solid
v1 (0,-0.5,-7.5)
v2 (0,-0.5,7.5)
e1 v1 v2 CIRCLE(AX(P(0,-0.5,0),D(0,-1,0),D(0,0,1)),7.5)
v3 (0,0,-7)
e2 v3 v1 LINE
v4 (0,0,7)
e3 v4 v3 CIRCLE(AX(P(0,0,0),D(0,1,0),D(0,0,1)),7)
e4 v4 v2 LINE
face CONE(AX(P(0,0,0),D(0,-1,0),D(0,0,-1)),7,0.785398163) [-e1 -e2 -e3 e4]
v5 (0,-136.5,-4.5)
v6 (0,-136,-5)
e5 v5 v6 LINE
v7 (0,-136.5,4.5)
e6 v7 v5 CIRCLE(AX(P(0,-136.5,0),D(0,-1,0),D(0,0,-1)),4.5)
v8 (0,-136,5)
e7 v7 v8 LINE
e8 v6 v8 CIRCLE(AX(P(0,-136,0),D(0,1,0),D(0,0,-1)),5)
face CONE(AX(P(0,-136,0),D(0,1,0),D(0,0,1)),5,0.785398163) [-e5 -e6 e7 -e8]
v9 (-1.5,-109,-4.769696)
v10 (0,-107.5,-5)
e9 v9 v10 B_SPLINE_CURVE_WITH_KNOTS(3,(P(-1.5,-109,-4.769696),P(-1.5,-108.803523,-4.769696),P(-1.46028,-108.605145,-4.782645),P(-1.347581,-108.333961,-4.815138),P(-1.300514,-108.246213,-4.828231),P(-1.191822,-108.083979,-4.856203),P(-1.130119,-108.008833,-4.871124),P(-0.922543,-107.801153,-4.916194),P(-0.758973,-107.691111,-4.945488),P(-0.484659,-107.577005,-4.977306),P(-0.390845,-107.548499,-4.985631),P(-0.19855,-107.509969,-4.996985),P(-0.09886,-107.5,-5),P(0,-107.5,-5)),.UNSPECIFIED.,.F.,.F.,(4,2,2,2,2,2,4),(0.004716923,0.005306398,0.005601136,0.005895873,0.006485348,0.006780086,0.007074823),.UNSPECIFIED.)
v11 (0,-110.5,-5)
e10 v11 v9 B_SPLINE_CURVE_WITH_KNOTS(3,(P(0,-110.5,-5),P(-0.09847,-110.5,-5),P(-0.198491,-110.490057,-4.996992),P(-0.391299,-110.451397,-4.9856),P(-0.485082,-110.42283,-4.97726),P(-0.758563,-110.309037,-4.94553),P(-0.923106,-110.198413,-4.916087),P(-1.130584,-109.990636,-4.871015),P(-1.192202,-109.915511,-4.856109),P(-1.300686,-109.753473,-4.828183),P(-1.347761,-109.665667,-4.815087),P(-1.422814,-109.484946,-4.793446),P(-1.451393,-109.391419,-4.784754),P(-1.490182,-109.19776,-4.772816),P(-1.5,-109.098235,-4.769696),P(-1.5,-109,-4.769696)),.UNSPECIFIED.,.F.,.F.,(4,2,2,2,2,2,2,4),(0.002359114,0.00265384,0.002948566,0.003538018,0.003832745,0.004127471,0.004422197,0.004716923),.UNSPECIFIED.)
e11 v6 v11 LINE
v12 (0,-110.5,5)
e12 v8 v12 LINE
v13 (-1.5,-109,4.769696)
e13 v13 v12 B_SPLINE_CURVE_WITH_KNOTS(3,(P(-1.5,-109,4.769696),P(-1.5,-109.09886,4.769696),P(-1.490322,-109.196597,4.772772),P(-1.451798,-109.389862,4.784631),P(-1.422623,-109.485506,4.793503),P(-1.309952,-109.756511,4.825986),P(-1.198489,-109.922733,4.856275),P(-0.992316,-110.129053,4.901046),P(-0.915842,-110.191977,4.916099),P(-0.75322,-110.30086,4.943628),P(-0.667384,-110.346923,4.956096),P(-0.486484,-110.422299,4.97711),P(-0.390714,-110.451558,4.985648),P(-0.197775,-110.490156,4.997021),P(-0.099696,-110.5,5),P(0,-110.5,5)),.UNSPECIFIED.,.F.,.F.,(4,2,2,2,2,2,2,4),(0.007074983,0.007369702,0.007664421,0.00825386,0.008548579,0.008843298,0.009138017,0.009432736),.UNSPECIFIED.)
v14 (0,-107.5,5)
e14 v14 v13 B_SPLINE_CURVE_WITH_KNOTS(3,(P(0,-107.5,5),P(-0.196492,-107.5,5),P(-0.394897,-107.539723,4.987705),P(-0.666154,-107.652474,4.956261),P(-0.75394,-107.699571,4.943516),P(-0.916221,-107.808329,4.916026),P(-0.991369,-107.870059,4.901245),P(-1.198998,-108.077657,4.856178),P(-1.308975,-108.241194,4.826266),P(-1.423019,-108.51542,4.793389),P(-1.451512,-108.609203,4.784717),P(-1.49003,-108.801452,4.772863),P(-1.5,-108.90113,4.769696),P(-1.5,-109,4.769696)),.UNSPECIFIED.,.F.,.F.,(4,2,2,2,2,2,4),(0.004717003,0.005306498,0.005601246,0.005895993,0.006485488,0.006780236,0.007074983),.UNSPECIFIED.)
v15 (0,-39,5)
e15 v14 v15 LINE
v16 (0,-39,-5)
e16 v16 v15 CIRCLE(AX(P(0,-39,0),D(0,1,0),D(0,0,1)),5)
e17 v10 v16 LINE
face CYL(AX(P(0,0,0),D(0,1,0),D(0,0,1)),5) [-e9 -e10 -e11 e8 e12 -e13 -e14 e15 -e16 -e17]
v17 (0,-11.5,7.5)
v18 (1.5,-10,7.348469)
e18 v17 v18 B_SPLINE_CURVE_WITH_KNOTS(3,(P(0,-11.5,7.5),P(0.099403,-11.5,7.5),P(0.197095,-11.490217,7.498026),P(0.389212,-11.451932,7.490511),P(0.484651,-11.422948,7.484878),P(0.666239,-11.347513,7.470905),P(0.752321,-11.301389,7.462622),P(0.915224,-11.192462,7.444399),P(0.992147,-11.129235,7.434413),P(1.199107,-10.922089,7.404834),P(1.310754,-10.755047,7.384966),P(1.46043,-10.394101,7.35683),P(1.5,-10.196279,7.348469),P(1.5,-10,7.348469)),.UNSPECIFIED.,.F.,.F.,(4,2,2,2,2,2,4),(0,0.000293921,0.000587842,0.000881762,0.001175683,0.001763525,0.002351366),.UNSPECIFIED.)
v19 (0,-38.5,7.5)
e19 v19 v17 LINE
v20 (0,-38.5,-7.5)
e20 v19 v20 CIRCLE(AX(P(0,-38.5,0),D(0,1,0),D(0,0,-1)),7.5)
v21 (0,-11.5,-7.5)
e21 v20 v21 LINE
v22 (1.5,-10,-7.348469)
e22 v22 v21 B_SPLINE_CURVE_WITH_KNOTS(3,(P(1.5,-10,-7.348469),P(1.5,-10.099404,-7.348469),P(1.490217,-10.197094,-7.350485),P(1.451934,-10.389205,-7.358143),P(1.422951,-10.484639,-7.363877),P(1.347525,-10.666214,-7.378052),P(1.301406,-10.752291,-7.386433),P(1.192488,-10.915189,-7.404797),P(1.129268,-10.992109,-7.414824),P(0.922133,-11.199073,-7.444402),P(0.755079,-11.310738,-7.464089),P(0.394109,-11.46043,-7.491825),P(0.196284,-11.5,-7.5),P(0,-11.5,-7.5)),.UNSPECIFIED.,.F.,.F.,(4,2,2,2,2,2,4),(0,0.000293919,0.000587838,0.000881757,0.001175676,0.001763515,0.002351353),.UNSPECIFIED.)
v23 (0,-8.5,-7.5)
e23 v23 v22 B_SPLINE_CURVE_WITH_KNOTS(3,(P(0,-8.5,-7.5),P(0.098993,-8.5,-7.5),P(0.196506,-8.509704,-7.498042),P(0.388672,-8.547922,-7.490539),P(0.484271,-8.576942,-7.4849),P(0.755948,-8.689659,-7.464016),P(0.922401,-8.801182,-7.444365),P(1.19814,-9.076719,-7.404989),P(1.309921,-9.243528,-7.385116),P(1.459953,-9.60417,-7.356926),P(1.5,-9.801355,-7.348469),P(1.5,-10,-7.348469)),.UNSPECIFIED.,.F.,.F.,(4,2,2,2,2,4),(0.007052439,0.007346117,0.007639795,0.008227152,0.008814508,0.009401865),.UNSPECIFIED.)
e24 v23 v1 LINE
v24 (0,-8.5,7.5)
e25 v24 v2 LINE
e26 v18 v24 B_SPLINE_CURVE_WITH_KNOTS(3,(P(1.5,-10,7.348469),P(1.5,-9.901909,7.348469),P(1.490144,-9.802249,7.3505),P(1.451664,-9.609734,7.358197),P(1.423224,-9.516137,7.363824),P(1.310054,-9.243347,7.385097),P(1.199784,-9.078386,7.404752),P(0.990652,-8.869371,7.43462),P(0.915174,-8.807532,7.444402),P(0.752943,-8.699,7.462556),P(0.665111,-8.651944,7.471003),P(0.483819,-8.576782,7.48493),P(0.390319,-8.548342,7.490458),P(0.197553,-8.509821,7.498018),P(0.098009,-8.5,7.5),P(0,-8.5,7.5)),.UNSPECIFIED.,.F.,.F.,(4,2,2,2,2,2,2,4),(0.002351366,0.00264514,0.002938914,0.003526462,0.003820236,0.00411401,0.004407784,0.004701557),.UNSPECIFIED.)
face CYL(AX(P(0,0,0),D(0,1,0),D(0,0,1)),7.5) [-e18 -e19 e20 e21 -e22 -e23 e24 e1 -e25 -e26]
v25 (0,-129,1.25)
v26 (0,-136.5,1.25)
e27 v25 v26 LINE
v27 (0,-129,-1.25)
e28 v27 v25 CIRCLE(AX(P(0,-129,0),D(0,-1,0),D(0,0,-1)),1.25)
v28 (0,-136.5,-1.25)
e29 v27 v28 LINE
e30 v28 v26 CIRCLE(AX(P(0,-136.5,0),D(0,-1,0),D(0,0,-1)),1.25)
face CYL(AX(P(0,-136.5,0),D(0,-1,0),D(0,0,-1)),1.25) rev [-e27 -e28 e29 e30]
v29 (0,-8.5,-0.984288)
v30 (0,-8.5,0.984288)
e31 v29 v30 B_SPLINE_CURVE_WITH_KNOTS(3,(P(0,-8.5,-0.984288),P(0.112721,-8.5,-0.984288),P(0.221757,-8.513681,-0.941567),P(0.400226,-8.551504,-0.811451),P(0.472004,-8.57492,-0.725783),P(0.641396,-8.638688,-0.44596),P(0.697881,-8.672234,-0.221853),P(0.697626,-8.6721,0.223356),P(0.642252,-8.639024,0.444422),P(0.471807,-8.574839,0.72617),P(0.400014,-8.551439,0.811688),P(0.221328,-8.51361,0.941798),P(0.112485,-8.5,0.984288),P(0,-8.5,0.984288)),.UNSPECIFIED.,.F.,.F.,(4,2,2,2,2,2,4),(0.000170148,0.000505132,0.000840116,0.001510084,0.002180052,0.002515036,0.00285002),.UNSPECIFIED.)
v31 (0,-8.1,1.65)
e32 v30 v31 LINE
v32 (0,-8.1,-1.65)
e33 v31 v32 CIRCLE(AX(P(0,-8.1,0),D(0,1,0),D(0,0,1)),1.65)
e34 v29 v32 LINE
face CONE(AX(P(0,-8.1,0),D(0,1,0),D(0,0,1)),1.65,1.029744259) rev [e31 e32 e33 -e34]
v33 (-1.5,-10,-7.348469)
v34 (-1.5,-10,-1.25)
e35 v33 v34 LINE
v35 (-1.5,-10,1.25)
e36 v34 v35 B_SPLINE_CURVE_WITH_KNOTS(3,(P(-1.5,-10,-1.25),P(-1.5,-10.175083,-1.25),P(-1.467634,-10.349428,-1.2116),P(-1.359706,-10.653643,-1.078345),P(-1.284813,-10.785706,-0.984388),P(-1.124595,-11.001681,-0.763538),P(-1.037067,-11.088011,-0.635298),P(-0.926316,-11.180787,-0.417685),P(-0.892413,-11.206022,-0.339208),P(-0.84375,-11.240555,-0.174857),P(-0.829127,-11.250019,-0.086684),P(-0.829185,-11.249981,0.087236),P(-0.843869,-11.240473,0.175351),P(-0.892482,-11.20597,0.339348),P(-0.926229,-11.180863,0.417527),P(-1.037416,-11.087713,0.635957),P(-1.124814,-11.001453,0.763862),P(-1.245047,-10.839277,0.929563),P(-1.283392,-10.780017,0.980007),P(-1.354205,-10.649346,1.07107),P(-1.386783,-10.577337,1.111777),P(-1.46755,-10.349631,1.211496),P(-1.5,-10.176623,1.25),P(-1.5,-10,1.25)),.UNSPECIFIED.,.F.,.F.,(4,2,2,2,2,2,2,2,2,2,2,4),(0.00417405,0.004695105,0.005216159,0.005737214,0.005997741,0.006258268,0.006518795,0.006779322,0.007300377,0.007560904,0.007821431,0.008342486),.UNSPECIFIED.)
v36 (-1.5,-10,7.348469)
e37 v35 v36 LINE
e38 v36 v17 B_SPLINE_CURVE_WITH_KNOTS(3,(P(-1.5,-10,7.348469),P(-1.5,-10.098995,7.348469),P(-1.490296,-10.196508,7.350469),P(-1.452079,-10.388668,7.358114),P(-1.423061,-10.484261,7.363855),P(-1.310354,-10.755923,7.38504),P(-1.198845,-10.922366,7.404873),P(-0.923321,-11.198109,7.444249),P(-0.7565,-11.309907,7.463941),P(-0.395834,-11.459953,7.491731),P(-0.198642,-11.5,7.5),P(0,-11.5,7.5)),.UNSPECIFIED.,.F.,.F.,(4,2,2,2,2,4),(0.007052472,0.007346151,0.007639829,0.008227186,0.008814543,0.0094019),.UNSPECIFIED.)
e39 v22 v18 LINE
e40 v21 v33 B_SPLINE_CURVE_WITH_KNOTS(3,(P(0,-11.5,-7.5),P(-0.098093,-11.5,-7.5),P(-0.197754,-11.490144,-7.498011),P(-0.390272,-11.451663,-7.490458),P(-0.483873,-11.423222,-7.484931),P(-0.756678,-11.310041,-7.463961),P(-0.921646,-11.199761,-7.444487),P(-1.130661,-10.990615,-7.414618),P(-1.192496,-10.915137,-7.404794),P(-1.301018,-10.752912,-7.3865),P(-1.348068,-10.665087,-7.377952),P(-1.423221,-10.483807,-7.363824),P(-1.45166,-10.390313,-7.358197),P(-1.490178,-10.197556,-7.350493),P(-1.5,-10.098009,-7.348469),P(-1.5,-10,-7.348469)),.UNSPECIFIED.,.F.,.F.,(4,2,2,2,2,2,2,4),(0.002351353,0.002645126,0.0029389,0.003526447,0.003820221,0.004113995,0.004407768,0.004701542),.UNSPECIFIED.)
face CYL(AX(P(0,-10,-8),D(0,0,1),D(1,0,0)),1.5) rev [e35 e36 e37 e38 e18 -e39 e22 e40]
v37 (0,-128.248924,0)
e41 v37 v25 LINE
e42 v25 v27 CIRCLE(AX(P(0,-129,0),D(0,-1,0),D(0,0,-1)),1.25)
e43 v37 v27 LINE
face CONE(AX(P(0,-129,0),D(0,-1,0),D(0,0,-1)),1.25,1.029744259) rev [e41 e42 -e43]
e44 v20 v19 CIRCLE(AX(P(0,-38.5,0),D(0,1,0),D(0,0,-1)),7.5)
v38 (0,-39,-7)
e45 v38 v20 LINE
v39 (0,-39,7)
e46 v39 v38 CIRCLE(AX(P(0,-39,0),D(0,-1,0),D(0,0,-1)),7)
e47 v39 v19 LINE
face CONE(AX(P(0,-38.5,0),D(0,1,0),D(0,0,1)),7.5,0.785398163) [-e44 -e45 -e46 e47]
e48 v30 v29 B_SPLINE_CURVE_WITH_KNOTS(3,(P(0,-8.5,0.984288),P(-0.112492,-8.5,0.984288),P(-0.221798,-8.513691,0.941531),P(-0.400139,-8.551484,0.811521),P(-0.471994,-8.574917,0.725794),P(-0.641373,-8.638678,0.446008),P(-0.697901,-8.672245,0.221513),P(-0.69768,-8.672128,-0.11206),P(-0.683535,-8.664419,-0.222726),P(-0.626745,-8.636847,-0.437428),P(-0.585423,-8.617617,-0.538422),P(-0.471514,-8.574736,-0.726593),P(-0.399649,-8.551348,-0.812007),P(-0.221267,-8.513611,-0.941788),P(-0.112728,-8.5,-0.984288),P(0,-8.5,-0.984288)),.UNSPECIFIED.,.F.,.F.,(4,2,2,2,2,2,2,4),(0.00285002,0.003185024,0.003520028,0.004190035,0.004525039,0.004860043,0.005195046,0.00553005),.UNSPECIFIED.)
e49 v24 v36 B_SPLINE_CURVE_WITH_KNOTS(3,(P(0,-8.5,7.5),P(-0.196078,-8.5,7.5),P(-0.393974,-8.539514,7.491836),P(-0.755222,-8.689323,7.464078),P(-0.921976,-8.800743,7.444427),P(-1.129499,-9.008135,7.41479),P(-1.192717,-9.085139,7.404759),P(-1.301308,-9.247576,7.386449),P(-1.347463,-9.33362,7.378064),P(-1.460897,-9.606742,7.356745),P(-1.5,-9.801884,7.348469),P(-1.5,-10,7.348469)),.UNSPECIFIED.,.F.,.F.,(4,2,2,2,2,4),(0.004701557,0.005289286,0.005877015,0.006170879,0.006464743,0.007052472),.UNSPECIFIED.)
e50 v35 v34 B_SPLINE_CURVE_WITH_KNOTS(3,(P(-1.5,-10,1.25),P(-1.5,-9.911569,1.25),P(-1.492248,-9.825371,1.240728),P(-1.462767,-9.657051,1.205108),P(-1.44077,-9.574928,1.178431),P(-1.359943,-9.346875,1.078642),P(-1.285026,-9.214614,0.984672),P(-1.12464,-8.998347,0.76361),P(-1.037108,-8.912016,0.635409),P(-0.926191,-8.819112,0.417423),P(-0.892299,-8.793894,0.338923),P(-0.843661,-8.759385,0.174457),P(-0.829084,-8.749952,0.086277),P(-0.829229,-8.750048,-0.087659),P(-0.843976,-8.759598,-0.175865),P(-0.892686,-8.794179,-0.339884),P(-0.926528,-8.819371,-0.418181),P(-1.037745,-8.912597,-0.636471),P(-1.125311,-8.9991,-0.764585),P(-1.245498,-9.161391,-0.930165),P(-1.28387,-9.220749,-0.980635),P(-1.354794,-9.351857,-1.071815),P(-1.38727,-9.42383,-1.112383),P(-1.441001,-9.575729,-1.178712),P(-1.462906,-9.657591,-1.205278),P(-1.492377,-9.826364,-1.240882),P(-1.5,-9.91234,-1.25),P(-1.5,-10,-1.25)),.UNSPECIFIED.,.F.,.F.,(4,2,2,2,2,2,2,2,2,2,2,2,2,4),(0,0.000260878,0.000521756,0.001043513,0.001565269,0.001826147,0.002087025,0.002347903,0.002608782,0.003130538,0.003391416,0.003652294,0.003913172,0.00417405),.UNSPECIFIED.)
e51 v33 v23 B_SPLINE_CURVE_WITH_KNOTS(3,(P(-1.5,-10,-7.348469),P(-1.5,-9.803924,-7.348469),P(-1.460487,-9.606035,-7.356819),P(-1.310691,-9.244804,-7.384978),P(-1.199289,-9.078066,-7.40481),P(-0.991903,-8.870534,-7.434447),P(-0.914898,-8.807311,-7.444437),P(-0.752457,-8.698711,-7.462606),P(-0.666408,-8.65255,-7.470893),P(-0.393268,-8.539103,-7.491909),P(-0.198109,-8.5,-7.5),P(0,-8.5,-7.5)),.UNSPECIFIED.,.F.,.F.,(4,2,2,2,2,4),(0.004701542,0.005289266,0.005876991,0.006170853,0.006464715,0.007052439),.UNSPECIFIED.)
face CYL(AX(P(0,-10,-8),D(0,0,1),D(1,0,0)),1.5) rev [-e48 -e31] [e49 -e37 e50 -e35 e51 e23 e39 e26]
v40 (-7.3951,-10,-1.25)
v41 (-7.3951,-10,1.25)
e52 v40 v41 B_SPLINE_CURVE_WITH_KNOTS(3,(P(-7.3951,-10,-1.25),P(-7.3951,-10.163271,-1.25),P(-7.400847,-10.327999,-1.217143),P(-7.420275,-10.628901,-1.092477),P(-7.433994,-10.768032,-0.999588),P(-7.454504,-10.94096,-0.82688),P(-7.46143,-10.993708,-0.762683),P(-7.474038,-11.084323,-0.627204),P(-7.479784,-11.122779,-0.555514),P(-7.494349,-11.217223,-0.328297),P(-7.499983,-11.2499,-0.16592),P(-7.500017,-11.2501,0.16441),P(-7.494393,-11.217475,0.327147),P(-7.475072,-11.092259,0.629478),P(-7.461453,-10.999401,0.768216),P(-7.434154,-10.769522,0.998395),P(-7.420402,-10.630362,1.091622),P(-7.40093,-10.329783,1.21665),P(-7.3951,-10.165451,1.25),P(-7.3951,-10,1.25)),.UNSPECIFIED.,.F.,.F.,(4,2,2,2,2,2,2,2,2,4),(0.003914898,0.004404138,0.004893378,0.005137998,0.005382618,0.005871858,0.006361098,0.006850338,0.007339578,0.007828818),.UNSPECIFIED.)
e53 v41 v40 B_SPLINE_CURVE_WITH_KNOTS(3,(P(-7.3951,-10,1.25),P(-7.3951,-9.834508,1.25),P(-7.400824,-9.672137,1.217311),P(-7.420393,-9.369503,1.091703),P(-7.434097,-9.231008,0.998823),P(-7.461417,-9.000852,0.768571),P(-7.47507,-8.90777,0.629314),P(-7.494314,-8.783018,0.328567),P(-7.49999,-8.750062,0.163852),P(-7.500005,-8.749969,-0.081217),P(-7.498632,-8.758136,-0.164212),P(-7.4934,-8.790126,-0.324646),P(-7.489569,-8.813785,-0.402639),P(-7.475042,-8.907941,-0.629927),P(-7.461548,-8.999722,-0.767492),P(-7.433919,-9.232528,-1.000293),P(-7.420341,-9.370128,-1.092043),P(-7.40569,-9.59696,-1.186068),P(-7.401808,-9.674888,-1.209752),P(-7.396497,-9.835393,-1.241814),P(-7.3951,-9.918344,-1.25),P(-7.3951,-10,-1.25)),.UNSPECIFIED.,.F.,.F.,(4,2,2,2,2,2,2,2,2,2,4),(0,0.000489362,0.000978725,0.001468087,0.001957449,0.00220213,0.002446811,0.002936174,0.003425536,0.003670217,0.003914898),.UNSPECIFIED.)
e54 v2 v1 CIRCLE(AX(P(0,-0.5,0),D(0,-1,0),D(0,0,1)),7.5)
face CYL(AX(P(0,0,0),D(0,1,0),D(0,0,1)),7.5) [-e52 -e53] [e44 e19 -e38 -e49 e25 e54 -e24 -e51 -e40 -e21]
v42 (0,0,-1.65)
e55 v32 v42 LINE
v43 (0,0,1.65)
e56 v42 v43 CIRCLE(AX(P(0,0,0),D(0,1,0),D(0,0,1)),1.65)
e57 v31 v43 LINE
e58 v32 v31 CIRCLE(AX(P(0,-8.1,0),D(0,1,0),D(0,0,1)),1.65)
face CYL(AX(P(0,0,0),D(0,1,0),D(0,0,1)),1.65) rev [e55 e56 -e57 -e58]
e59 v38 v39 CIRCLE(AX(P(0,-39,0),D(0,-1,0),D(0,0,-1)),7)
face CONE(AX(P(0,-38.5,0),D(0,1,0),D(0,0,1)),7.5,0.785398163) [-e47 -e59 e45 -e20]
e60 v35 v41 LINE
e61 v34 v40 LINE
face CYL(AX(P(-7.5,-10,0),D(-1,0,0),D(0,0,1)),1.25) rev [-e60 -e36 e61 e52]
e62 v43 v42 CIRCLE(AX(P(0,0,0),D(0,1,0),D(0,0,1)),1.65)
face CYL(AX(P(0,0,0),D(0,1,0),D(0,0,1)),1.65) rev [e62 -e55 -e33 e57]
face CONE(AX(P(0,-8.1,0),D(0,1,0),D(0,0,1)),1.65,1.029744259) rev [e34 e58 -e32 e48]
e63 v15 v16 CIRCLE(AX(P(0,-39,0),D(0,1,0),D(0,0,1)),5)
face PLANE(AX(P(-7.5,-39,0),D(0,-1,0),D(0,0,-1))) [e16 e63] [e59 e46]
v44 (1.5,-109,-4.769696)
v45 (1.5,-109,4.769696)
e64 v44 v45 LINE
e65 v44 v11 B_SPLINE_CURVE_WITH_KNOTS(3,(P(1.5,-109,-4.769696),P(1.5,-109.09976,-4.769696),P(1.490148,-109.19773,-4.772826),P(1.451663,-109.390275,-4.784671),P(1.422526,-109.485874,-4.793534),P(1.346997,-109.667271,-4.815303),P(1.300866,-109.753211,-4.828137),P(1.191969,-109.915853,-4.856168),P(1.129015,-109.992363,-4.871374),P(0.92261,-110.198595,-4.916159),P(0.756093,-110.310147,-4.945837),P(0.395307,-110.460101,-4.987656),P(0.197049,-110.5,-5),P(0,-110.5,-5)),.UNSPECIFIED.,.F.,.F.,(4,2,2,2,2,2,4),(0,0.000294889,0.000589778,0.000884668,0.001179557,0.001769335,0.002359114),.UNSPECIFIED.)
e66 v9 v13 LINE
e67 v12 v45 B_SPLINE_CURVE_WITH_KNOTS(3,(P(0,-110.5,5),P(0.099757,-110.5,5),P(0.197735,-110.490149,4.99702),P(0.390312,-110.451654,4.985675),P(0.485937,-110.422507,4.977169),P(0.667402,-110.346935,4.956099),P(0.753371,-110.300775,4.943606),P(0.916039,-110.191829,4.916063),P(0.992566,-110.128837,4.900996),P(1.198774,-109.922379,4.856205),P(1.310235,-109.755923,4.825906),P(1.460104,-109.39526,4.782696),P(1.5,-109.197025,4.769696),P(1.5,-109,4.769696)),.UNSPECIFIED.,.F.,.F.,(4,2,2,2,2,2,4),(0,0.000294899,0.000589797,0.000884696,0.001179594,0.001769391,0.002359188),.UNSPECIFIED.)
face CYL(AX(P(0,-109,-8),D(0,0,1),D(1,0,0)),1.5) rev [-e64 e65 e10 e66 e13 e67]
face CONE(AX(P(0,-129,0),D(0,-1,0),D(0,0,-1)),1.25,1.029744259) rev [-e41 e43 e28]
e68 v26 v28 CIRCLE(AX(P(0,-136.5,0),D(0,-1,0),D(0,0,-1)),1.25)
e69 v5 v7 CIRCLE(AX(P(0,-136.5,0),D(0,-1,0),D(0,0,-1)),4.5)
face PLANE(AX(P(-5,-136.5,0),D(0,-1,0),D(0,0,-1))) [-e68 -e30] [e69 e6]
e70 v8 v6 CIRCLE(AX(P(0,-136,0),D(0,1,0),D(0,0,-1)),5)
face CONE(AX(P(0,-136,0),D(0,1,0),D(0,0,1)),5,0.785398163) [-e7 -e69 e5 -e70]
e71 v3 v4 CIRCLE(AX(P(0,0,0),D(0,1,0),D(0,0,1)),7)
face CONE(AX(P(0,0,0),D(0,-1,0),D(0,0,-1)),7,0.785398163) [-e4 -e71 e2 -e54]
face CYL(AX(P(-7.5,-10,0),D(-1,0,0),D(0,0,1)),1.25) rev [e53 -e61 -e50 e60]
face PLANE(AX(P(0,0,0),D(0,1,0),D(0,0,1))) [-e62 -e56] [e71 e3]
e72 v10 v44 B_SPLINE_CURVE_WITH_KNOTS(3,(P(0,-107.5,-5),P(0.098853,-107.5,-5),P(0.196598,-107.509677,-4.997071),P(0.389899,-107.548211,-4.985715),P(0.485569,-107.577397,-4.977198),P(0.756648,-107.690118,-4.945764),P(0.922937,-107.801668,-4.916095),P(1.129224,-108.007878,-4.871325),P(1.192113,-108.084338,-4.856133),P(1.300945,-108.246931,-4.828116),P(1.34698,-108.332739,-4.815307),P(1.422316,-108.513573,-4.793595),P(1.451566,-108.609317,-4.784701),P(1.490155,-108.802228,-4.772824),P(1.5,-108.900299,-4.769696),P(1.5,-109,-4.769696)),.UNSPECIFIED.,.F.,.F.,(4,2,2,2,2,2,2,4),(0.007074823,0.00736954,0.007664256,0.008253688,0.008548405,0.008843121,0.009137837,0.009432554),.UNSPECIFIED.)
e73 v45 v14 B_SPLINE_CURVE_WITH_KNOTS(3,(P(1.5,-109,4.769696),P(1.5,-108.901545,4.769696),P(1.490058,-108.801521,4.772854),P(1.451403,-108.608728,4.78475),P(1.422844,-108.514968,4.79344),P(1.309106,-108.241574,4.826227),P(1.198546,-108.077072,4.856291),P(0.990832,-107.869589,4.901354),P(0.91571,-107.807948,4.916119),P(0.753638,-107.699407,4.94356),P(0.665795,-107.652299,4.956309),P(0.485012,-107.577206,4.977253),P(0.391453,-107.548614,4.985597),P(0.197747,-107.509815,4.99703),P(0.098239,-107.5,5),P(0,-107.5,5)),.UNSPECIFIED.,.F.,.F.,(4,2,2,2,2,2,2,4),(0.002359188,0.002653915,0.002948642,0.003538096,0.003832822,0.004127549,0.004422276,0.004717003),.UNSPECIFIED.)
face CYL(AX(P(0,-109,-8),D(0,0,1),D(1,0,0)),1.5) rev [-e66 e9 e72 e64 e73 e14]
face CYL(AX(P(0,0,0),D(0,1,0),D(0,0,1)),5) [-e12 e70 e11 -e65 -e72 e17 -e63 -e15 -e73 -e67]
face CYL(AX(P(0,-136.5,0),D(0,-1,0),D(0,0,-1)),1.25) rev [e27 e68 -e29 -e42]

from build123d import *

# Parameters (mm, degrees)
M4_TAPPED_HOLE1_D     = 3.3
M4_TAPPED_HOLE1_DEPTH = 8.1
M4_TAPPED_HOLE1_TIP   = 0.991420021
SKETCH3_R             = 1.5
CUT_EXTRUDE1_DEPTH    = 8
M3_TAPPED_HOLE2_D     = 2.5
M3_TAPPED_HOLE2_DEPTH = 7.5
M3_TAPPED_HOLE2_TIP   = 0.751075774
CHAMFER1_SIZE         = 0.5
M3_TAPPED_HOLE3_D     = 2.5
M3_TAPPED_HOLE3_DEPTH = 7.5
M3_TAPPED_HOLE3_TIP   = 0.751075774
SKETCH9_R             = 1.5
CUT_EXTRUDE2_DEPTH    = 8


with BuildPart() as part:
    # Sketch1 → Revolve1 (revolve)
    with BuildSketch(Plane.XY, mode=Mode.PRIVATE) as revolve1_sk:
        Polygon((0, 0), (-7.5, 0), (-7.5, -39), (-5, -39), (-5, -136.5), (0, -136.5), align=None)
    revolve(revolve1_sk.sketch.rotate(Axis((0, 0, 0), (0, -1, 0)), 270), axis=Axis((0, 0, 0), (0, -1, 0)))

    # M4 Tapped Hole1
    with Locations(Plane.ZX):
        with Locations((0, 0)):
            Hole(M4_TAPPED_HOLE1_D / 2, depth=M4_TAPPED_HOLE1_DEPTH)
            with Locations((0, 0, -(M4_TAPPED_HOLE1_DEPTH + M4_TAPPED_HOLE1_TIP / 2))):  # 118° drill point
                Cone(0, M4_TAPPED_HOLE1_D / 2, M4_TAPPED_HOLE1_TIP, mode=Mode.SUBTRACT)

    # Sketch3 → Cut-Extrude1 (cut, symmetric)
    with BuildSketch(Plane.XY):
        with Locations((0, -10)):
            Circle(SKETCH3_R)
    extrude(amount=CUT_EXTRUDE1_DEPTH, both=True, mode=Mode.SUBTRACT)

    # M3 Tapped Hole2
    with Locations(Plane(origin=(0, -136.5, 0), x_dir=(0, 0, -1), z_dir=(0, -1, 0))):
        with Locations((0, 0)):
            Hole(M3_TAPPED_HOLE2_D / 2, depth=M3_TAPPED_HOLE2_DEPTH)
            with Locations((0, 0, -(M3_TAPPED_HOLE2_DEPTH + M3_TAPPED_HOLE2_TIP / 2))):  # 118° drill point
                Cone(0, M3_TAPPED_HOLE2_D / 2, M3_TAPPED_HOLE2_TIP, mode=Mode.SUBTRACT)

    # Chamfer1
    chamfer1_edges = [part.edges().sort_by_distance(p)[0] for p in [
        (0, -136.5, -5),
        (0, -39, -7.5),
        (0, 0, -7.5),
    ]]
    chamfer(chamfer1_edges, length=CHAMFER1_SIZE)

    # M3 Tapped Hole3
    with Locations(Plane(origin=(-7.5, -10, 0), x_dir=(0, 0, -1), z_dir=(-1, 0, 0))):
        with Locations((0, 0)):
            Hole(M3_TAPPED_HOLE3_D / 2, depth=M3_TAPPED_HOLE3_DEPTH)
            with Locations((0, 0, -(M3_TAPPED_HOLE3_DEPTH + M3_TAPPED_HOLE3_TIP / 2))):  # 118° drill point
                Cone(0, M3_TAPPED_HOLE3_D / 2, M3_TAPPED_HOLE3_TIP, mode=Mode.SUBTRACT)

    # Sketch9 → Cut-Extrude2 (cut, symmetric)
    with BuildSketch(Plane.XY):
        with Locations((0, -109)):
            Circle(SKETCH9_R)
    extrude(amount=CUT_EXTRUDE2_DEPTH, both=True, mode=Mode.SUBTRACT)


solid = part.part
